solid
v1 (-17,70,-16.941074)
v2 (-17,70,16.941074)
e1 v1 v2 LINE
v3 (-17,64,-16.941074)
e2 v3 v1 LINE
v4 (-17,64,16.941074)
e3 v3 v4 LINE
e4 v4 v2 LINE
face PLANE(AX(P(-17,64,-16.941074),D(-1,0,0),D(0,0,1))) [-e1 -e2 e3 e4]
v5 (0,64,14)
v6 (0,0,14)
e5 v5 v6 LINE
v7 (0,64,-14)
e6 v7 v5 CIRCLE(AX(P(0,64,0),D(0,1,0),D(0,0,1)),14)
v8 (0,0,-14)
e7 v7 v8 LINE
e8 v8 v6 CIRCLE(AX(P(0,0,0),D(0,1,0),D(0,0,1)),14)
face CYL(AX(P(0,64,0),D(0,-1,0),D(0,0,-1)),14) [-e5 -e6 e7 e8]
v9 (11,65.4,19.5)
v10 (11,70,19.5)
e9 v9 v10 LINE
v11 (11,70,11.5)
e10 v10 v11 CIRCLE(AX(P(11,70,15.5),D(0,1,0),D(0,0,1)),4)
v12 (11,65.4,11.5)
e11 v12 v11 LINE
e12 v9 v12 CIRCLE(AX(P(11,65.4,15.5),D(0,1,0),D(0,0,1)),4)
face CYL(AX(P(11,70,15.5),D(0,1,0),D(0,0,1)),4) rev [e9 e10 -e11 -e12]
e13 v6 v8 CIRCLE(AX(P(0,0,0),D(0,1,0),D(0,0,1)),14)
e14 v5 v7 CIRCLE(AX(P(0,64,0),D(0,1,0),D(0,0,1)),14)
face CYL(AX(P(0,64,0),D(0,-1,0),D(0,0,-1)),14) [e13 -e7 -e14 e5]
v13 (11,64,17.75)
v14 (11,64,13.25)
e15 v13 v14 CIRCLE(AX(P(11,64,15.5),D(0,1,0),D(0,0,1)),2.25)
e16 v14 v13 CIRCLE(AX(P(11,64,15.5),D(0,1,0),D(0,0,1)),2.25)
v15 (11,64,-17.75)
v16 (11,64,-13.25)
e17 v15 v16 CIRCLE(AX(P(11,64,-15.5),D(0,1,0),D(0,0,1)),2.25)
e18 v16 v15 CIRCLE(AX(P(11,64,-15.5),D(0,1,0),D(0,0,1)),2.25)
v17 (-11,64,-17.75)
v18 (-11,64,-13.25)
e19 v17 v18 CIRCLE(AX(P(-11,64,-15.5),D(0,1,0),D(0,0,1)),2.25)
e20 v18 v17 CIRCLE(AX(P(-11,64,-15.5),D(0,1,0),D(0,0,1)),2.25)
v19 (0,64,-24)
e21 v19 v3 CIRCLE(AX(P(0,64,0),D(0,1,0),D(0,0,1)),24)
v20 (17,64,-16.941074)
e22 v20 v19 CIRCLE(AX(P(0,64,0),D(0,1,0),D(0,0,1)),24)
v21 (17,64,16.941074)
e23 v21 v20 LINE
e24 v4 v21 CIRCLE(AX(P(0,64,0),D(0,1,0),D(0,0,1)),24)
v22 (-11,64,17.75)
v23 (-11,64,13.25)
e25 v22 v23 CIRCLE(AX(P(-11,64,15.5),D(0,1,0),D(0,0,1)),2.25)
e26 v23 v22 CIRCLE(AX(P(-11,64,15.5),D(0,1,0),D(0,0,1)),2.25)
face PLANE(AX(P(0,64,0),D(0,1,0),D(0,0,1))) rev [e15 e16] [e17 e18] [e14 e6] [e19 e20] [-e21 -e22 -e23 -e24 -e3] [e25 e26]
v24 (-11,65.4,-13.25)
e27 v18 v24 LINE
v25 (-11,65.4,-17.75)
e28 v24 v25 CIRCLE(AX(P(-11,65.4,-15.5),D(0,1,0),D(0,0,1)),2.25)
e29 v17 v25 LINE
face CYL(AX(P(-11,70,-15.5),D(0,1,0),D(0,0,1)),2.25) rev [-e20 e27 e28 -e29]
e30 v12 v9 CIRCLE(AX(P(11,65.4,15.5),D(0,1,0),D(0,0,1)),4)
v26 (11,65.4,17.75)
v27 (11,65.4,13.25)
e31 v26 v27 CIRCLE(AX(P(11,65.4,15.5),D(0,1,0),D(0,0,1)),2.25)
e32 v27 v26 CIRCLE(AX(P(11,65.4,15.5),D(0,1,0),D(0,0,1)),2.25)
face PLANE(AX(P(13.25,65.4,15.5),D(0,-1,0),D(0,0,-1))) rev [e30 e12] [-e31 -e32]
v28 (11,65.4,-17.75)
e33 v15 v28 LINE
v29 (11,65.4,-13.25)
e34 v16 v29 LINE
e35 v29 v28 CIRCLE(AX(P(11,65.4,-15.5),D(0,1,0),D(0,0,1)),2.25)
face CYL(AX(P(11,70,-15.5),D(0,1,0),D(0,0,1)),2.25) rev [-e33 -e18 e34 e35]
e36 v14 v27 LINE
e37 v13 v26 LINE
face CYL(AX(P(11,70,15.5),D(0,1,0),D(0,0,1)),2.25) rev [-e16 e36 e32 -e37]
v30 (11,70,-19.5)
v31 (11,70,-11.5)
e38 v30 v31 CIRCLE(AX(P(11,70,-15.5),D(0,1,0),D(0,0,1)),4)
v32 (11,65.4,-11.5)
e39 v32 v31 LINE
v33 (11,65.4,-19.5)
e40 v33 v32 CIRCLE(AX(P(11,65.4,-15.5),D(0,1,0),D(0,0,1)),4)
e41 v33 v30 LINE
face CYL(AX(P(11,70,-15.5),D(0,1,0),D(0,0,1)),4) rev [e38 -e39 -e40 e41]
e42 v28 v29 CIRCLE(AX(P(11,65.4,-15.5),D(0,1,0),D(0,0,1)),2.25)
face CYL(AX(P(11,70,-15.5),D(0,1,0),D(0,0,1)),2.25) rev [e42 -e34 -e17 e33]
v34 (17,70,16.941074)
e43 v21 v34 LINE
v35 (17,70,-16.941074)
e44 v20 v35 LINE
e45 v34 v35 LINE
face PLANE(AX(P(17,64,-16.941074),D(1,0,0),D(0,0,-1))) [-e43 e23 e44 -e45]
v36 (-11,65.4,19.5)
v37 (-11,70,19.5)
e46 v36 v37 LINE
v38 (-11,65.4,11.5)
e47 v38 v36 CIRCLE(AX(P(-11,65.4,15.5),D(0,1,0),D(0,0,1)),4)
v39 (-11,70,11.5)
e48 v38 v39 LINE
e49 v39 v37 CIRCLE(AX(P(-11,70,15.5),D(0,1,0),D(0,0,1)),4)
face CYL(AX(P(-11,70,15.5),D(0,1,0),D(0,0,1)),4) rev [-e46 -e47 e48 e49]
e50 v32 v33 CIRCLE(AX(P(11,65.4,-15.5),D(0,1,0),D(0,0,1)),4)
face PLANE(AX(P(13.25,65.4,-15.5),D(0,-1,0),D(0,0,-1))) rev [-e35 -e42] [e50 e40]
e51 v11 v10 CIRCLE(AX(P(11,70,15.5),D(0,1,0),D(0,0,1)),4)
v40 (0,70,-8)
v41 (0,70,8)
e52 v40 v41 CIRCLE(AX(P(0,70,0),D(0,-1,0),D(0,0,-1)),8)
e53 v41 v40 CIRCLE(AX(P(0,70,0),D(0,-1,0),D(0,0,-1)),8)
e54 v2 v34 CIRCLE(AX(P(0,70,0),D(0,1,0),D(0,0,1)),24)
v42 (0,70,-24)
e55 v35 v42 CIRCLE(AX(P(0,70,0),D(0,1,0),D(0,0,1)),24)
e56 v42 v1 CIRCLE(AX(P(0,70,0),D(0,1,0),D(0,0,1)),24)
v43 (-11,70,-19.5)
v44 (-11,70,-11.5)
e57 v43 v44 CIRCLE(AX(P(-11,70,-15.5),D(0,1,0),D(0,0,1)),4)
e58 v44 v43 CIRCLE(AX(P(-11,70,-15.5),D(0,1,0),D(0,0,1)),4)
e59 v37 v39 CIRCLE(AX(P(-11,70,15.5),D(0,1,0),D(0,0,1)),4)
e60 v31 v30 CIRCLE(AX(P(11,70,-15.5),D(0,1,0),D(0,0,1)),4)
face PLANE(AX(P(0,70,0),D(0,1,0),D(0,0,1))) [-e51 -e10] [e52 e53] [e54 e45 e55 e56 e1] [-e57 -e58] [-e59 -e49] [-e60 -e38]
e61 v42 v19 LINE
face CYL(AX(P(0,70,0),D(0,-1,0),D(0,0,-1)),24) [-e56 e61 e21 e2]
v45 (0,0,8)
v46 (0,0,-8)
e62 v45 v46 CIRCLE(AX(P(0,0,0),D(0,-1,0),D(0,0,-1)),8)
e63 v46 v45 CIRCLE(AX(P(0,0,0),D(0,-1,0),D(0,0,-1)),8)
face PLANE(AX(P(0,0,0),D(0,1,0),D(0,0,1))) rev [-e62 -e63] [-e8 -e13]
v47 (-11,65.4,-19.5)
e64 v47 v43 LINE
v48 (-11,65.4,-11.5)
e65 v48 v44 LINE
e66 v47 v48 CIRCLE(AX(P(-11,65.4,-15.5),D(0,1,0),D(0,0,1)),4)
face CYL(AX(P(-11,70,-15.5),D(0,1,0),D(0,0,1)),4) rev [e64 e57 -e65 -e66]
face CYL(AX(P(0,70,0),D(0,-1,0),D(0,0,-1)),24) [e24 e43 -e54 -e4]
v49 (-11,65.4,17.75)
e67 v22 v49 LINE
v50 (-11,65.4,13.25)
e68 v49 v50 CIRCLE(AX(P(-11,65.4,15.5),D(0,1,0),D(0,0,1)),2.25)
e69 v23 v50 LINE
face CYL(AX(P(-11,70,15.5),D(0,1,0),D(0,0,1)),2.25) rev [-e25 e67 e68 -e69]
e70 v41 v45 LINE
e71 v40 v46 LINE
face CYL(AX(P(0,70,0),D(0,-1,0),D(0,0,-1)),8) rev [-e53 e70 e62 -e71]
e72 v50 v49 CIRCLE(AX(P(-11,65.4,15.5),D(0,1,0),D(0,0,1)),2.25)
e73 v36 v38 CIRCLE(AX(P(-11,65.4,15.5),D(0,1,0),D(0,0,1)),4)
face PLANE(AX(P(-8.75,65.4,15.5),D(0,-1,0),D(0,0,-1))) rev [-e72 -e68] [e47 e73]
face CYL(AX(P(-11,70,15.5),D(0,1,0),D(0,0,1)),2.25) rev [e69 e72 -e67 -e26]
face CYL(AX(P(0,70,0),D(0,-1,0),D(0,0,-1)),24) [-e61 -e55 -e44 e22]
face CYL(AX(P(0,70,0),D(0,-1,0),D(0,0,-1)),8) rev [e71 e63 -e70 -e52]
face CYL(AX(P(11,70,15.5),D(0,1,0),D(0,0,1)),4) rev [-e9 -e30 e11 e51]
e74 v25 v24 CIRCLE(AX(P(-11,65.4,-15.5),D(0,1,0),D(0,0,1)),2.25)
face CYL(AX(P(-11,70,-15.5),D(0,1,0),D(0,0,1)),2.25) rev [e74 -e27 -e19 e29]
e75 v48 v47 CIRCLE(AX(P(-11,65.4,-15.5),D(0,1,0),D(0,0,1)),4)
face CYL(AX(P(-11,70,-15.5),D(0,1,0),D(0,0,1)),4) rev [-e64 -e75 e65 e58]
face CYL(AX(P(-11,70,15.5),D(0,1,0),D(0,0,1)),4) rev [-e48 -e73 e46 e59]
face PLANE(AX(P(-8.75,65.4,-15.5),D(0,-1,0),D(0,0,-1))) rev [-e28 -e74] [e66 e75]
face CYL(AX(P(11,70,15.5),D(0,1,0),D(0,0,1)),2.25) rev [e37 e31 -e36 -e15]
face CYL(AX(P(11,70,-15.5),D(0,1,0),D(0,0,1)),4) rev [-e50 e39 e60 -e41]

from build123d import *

# Parameters (mm, degrees)
SKETCH1_R                                            = 14
BOSS_EXTRUDE1_DEPTH                                  = 64
SKETCH2_R                                            = 24
BOSS_EXTRUDE2_DEPTH                                  = 6
SKETCH3_OUTSIDE_W                                    = 69.502
SKETCH3_OUTSIDE_H                                    = 69.502
CUT_EXTRUDE2_DEPTH                                   = 6
SKETCH4_R                                            = 8
CUT_EXTRUDE3_DEPTH                                   = 76.927597091
HOLE_SIZE_PER_SOCKET_HEAD_CAP_SCREW_TYPE_D           = 4.5
HOLE_SIZE_PER_SOCKET_HEAD_CAP_SCREW_TYPE_CBORE_D     = 8
HOLE_SIZE_PER_SOCKET_HEAD_CAP_SCREW_TYPE_CBORE_DEPTH = 4.6


with BuildPart() as part:
    # Sketch1 → Boss-Extrude1 (new body)
    with BuildSketch(Plane(origin=(0, 0, 0), x_dir=(1, 0, 0), z_dir=(0, 1, 0))):
        with Locations(Location((0, 0, 0), (0, 0, 270))):
            Circle(SKETCH1_R)
    extrude(amount=BOSS_EXTRUDE1_DEPTH)

    # Sketch2 → Boss-Extrude2 (add)
    with BuildSketch(Plane(origin=(0, 64, 0), x_dir=(1, 0, 0), z_dir=(0, 1, 0))):
        with Locations(Location((0, 0, 0), (0, 0, 270))):
            Circle(SKETCH2_R)
    extrude(amount=BOSS_EXTRUDE2_DEPTH)

    # Sketch3 outside → Cut-Extrude2 (cut)
    with BuildSketch(Plane(origin=(0, 70, 0), x_dir=(1, 0, 0), z_dir=(0, 1, 0))):
        Rectangle(SKETCH3_OUTSIDE_W, SKETCH3_OUTSIDE_H)
        with BuildLine():
            Line((-17, 16.941074346), (-17, -16.941074346))
            ThreePointArc((-17, -16.941074346), (0, -24), (17, -16.941074346))
            Line((17, -16.941074346), (17, 16.941074346))
            ThreePointArc((17, 16.941074346), (0, 24), (-17, 16.941074346))
        make_face(mode=Mode.SUBTRACT)
    extrude(amount=-CUT_EXTRUDE2_DEPTH, mode=Mode.SUBTRACT)

    # Sketch4 → Cut-Extrude3 (cut, through all)
    with BuildSketch(Plane.XZ):
        with Locations(Location((0, 0, 0), (0, 0, 270))):
            Circle(SKETCH4_R)
    extrude(amount=-CUT_EXTRUDE3_DEPTH, mode=Mode.SUBTRACT)

    # Hole size per socket head cap screw type1 (through all)
    with Locations(Plane(origin=(0, 70, 0), x_dir=(-1, 0, 0), z_dir=(0, 1, 0))):
        with Locations((-11, 15.5), (11, 15.5), (11, -15.5), (-11, -15.5)):
            CounterBoreHole(HOLE_SIZE_PER_SOCKET_HEAD_CAP_SCREW_TYPE_D / 2, HOLE_SIZE_PER_SOCKET_HEAD_CAP_SCREW_TYPE_CBORE_D / 2, HOLE_SIZE_PER_SOCKET_HEAD_CAP_SCREW_TYPE_CBORE_DEPTH)


solid = part.part
